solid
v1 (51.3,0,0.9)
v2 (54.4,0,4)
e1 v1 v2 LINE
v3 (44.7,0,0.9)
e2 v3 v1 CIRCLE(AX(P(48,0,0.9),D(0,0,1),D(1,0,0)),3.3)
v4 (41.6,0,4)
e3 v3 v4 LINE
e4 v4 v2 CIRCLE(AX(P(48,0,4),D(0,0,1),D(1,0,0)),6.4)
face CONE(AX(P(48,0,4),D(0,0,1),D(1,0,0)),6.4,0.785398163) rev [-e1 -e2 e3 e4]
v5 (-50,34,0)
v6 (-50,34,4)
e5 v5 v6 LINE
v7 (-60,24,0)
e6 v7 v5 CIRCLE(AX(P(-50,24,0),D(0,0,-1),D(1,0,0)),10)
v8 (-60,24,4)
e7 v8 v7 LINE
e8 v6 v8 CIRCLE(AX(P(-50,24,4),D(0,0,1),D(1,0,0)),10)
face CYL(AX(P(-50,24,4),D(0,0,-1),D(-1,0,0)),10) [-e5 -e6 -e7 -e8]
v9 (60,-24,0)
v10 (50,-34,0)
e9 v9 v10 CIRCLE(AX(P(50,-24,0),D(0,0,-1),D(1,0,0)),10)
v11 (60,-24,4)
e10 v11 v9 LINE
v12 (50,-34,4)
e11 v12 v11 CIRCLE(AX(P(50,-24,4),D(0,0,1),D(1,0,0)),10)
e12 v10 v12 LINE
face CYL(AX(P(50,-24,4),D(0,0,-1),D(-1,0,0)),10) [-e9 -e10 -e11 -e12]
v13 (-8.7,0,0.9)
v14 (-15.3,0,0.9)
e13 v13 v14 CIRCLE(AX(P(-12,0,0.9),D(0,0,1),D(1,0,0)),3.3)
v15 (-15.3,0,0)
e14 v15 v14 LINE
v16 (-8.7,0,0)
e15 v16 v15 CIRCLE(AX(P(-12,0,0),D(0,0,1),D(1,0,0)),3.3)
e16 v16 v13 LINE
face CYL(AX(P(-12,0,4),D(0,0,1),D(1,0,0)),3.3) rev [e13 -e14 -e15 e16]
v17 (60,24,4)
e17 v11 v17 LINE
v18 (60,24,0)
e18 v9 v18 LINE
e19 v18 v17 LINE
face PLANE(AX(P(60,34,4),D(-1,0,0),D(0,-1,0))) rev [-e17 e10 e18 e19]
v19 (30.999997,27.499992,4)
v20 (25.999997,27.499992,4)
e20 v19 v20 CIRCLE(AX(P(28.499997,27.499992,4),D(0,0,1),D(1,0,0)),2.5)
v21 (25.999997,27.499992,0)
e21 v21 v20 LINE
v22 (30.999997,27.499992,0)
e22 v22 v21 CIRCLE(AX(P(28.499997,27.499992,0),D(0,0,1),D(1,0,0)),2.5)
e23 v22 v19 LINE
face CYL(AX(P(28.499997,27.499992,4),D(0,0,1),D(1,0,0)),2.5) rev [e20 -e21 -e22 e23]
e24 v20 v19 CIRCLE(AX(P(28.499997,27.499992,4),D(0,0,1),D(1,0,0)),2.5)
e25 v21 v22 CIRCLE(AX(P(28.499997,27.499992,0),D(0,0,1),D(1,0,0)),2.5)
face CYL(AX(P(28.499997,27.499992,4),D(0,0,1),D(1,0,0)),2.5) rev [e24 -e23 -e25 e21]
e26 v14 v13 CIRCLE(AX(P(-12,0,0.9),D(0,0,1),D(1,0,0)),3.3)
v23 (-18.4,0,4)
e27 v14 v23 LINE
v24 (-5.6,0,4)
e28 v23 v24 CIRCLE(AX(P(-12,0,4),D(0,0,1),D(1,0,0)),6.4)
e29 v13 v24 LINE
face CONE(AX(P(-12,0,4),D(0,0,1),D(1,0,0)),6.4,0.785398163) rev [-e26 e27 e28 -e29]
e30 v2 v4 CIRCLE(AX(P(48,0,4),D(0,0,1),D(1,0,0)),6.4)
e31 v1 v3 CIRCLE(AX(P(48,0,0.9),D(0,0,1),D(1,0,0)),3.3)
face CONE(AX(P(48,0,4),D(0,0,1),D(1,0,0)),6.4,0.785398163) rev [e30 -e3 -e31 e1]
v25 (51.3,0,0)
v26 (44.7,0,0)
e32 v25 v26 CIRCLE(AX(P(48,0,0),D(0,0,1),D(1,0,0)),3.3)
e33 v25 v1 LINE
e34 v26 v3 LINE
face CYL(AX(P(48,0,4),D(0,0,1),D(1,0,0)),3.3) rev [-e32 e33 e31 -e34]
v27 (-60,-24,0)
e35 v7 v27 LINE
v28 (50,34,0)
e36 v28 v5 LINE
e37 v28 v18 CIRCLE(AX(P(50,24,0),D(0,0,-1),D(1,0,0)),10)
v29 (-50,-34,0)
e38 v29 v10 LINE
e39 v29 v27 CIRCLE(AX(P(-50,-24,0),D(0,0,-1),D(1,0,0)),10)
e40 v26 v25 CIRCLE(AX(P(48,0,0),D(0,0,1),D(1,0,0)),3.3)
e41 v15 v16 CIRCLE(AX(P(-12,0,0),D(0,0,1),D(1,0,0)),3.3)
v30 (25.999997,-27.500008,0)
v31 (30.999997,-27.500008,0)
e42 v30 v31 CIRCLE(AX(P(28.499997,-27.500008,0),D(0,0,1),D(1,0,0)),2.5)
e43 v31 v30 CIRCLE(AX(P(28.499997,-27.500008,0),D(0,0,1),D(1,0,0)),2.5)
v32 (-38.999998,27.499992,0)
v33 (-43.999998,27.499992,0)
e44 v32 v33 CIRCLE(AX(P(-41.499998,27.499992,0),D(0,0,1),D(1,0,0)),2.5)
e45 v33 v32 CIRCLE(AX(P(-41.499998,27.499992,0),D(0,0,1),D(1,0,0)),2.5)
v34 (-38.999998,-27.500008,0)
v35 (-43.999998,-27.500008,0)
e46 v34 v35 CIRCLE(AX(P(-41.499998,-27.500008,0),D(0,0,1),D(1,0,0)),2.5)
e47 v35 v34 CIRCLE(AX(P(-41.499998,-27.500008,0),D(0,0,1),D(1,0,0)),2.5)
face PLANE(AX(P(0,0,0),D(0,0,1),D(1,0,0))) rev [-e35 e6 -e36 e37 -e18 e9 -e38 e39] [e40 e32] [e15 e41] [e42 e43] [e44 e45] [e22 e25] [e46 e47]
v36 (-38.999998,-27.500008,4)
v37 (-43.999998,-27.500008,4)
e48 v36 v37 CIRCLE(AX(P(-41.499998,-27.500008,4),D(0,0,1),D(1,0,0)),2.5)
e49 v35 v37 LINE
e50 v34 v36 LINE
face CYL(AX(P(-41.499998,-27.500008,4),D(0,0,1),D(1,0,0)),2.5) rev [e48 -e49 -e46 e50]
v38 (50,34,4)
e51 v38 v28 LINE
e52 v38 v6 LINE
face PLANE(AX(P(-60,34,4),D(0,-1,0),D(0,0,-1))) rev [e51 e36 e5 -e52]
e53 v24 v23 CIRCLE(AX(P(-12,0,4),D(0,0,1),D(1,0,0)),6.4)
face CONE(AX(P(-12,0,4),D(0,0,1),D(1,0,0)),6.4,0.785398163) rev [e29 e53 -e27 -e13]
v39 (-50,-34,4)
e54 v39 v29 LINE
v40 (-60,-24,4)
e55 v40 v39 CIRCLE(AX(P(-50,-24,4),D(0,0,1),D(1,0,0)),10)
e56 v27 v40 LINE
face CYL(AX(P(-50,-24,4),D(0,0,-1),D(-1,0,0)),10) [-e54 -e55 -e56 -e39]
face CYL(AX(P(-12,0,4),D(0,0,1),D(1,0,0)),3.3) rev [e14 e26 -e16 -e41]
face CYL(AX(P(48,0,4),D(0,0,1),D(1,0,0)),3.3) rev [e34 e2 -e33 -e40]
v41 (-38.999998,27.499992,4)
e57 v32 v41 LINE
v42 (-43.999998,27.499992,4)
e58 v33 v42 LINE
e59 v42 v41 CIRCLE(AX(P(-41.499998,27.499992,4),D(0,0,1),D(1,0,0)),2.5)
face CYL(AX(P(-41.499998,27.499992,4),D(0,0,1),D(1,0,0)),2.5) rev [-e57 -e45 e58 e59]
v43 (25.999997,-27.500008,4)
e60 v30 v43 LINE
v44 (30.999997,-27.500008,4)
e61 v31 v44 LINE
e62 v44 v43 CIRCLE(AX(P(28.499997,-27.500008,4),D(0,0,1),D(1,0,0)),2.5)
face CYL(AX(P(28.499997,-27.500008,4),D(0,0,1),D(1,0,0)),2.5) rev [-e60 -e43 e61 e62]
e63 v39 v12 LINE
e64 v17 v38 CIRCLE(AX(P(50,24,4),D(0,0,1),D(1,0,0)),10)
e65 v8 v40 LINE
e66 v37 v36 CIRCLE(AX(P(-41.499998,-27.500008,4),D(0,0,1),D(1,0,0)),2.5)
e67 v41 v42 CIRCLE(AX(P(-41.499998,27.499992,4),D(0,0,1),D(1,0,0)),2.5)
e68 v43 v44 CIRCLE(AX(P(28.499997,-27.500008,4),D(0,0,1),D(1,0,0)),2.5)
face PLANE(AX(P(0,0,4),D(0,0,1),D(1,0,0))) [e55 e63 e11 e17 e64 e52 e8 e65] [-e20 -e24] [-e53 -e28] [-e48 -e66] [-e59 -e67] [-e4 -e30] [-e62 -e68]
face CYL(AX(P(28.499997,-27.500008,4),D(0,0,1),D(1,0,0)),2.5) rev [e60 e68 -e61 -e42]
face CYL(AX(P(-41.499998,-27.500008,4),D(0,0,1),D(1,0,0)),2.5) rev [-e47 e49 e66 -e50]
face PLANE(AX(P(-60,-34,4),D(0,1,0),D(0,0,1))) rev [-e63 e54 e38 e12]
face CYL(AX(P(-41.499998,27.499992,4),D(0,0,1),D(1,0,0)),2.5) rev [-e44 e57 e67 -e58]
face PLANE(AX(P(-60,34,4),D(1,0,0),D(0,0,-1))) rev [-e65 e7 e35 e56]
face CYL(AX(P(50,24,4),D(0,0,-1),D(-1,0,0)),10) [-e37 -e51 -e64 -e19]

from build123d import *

# Parameters (mm, degrees)
SKETCH_1_W               = 120
SKETCH_1_H               = 68
EXTRUDE_1_DEPTH          = 4
HOLE_WIZARD_M6_1_D       = 5
FILLET_1_R               = 10
HOLE_WIZARD_3_AT_2_COUNT = 2
HOLE_WIZARD_3_AT_2_PITCH = 60


with BuildPart() as part:
    # 草图1 → 凸台-拉伸1 (new body)
    with BuildSketch(Plane.XY):
        Rectangle(SKETCH_1_W, SKETCH_1_H)
    extrude(amount=EXTRUDE_1_DEPTH)

    # M6 螺纹孔1 (through all)
    with Locations(Plane.XY.offset(4)):
        with Locations((28.49999693, -27.500007889), (-41.499997526, 27.499992111), (-41.499997526, -27.500007889), (28.49999693, 27.499992111)):
            Hole(HOLE_WIZARD_M6_1_D / 2)

    # 圆角1
    fillet_1_edges = [part.edges().sort_by_distance(p)[0] for p in [
        (60, -34, 2),
        (-60, -34, 2),
        (-60, 34, 2),
        (60, 34, 2),
    ]]
    fillet(fillet_1_edges, radius=FILLET_1_R)

    # 草图9 → 打孔尺寸(%根据)内六角花形半沉头螺钉的类型3 (revolve, cut)
    with BuildSketch(Plane(origin=(-12, 0, 4), x_dir=(0, -1, 0), z_dir=(1, 0, 0))):
        Polygon((0, 0), (0, 4), (3.3, 4), (3.3, 3.1), (6.4, 0), align=None)
    hole_wizard_3 = revolve(axis=Axis((-12, 0, 10.35), (0, 0, -1)), mode=Mode.SUBTRACT)

    # 打孔尺寸(%根据)内六角花形半沉头螺钉的类型3 at 2: 打孔尺寸(%根据)内六角花形半沉头螺钉的类型3 ×2
    with Locations(*[(i * HOLE_WIZARD_3_AT_2_PITCH, 0, 0) for i in range(1, HOLE_WIZARD_3_AT_2_COUNT)]):
        add(hole_wizard_3, mode=Mode.SUBTRACT)


solid = part.part
